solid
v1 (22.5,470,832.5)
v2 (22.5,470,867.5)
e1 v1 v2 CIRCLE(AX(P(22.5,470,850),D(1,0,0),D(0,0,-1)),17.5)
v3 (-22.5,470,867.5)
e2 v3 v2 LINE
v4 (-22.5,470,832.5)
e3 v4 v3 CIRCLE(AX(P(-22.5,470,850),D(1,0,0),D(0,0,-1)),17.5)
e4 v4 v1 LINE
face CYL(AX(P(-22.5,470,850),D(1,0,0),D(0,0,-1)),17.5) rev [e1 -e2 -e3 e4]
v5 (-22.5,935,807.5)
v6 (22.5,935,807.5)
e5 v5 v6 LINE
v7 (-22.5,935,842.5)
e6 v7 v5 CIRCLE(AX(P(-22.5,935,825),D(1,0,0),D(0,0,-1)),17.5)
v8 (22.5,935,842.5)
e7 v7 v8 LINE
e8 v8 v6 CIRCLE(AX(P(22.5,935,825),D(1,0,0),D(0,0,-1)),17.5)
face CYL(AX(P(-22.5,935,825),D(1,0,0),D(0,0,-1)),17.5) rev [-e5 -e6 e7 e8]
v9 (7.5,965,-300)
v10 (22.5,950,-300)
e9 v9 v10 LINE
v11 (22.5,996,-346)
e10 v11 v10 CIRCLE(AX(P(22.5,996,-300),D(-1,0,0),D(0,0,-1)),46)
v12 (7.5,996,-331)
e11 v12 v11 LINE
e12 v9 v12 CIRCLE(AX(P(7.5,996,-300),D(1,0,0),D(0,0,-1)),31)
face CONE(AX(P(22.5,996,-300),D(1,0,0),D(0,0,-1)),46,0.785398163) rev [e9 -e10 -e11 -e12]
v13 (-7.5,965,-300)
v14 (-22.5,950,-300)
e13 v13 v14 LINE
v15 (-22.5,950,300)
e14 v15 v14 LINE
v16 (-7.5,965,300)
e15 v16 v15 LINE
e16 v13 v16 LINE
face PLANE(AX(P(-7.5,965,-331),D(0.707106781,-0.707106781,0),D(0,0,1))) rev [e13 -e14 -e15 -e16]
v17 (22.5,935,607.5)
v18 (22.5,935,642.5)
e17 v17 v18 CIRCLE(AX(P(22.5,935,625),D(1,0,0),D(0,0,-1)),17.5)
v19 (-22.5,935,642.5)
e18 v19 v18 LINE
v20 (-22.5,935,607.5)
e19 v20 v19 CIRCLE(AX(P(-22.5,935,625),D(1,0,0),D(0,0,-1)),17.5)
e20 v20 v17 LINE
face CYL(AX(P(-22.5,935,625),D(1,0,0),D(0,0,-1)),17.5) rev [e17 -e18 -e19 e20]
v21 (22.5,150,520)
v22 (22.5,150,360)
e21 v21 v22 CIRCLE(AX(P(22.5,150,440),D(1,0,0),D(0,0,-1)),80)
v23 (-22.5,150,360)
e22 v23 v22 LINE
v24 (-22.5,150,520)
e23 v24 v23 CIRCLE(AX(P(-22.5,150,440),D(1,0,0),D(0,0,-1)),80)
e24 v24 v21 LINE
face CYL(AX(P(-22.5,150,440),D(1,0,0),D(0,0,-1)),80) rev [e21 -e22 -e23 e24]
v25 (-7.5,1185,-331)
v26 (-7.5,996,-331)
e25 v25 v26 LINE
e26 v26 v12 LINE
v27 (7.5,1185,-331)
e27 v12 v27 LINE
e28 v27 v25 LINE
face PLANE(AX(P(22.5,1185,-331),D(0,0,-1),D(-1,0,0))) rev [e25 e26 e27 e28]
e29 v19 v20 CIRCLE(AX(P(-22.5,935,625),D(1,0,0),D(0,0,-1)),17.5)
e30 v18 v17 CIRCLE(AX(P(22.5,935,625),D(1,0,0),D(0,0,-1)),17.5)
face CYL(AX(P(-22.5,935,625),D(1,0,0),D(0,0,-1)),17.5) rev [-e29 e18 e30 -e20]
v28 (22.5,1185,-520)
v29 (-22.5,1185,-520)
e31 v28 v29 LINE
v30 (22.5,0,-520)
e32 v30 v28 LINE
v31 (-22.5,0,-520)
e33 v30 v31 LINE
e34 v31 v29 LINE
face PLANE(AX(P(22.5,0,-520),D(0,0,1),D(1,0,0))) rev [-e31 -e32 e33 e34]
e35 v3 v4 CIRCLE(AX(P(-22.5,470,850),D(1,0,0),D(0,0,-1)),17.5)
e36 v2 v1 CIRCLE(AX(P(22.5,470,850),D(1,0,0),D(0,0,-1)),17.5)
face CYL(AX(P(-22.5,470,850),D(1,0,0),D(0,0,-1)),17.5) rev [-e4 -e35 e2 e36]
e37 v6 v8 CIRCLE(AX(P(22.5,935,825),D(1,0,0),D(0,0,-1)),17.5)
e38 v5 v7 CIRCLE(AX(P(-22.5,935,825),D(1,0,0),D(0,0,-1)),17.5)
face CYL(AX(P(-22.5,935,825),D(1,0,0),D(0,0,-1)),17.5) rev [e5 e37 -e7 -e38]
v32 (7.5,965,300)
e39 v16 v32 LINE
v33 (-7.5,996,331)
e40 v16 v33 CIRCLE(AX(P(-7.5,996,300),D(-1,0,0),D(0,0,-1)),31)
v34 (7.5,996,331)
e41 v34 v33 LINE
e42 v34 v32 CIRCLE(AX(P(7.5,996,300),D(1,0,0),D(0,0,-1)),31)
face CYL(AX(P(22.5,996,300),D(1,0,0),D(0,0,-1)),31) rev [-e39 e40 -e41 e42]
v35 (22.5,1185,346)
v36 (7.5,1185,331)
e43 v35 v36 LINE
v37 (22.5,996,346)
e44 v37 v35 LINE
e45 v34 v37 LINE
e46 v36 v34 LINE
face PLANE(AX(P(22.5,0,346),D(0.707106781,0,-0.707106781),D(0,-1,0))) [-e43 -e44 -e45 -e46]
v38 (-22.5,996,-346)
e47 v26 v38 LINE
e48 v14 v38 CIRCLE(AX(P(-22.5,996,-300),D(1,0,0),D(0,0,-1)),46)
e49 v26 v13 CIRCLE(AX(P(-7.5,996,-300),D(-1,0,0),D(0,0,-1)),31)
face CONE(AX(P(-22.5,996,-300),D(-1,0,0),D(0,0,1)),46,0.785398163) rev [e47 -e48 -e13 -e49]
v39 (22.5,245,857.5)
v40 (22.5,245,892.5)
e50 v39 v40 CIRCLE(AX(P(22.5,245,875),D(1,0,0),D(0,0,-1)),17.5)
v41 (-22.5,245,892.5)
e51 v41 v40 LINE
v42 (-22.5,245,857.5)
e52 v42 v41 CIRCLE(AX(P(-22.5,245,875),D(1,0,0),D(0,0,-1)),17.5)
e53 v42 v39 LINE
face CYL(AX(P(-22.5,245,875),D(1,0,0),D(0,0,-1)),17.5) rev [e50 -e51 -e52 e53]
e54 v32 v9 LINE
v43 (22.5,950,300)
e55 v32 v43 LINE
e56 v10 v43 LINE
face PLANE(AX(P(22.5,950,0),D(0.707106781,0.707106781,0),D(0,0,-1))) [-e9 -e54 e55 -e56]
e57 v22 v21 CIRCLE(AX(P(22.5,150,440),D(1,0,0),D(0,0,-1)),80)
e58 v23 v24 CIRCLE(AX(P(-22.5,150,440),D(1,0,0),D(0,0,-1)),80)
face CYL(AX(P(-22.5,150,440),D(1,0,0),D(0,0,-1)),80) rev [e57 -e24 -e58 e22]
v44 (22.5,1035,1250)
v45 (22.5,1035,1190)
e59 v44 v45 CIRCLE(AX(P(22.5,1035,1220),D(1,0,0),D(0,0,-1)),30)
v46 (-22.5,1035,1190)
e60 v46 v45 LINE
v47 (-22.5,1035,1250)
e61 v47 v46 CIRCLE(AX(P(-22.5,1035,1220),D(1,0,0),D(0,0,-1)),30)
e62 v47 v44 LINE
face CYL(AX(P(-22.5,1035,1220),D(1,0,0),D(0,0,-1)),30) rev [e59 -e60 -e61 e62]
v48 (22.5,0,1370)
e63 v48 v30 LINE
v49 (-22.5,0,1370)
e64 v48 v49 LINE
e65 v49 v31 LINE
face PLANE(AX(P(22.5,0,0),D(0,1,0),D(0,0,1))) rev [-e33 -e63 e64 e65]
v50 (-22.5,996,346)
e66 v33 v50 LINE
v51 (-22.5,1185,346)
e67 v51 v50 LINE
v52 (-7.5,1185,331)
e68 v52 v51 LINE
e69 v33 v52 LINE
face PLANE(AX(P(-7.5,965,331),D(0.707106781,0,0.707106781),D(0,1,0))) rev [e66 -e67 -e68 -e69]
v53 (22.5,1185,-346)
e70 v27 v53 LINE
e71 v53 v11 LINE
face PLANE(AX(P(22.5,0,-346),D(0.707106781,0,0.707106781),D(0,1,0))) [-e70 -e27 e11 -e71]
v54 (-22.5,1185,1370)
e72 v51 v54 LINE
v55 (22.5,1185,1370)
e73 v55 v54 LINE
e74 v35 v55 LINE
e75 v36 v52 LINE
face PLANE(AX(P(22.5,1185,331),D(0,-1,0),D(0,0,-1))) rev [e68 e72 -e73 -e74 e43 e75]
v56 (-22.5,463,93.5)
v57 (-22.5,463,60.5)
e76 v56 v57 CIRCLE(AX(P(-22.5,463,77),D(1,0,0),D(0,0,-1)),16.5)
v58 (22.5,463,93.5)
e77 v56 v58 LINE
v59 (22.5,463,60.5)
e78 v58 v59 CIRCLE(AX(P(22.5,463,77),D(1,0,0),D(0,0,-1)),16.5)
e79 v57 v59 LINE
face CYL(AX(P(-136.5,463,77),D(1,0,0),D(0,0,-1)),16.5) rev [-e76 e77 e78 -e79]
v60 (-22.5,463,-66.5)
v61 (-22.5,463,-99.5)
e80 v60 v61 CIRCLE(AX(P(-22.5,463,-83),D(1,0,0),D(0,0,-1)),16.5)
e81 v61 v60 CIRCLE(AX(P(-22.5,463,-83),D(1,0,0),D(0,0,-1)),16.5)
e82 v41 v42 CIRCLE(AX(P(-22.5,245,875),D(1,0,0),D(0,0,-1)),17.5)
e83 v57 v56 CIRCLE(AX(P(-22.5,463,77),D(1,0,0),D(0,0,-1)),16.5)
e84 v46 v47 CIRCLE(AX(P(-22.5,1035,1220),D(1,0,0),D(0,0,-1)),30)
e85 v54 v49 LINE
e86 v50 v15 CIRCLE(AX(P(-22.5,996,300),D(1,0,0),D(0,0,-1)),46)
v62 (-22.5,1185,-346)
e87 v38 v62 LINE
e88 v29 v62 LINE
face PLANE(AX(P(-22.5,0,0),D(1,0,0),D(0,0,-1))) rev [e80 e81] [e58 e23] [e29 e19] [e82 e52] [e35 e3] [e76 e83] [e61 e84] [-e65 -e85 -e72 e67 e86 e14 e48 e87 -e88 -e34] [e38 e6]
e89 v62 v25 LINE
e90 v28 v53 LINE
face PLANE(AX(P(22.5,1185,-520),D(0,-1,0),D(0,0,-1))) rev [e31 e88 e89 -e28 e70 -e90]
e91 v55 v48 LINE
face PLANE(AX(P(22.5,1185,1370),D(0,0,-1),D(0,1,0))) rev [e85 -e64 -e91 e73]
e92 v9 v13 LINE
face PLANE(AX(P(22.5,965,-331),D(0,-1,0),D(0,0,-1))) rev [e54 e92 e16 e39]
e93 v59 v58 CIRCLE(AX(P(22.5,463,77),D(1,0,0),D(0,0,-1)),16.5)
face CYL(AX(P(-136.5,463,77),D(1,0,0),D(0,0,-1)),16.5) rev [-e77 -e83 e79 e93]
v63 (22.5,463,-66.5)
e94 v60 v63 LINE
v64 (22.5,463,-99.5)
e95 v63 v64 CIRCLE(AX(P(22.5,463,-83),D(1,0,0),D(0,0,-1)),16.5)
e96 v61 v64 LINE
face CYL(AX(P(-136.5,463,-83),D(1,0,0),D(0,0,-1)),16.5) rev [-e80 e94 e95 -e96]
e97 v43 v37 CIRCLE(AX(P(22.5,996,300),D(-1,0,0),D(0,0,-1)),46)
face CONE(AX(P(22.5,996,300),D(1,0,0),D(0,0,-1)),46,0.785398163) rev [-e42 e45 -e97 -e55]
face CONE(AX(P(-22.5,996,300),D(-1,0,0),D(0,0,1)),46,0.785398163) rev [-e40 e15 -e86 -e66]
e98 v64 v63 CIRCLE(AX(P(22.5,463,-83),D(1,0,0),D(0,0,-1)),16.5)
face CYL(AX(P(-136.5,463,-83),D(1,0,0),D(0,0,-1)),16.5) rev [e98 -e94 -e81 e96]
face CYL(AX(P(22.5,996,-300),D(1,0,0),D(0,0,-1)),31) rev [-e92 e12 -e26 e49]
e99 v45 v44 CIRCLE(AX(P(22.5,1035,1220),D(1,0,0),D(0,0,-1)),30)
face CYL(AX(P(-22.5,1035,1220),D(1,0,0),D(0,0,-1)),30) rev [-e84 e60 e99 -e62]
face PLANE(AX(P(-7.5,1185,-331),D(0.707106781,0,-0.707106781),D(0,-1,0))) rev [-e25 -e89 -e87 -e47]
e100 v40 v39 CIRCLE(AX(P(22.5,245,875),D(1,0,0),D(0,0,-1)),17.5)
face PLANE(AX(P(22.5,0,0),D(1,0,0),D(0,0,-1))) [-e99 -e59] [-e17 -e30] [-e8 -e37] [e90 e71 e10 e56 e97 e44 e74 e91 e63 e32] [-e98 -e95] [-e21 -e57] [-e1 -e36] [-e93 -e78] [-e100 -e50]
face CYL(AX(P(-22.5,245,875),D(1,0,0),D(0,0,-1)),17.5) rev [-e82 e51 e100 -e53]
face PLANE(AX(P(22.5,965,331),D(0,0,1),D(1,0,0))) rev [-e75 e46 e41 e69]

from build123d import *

# Parameters (mm, degrees)
BOSS_EXTRUDE1_DEPTH = 22.5
SKETCH2_R           = 30
SKETCH2_R_2         = 17.5
SKETCH2_R_3         = 80
CUT_EXTRUDE1_DEPTH  = 1812.9464672
FILLET1_R           = 31
CHAMFER1_SIZE       = 15
SKETCH3_R           = 16.5
CUT_EXTRUDE2_DEPTH  = 159


with BuildPart() as part:
    # Sketch1 → Boss-Extrude1 (new, symmetric)
    with BuildSketch(Plane(origin=(0, 0, 0), x_dir=(0, 0, -1), z_dir=(1, 0, 0))):
        Polygon((0, 0), (520, 0), (520, 1185), (331, 1185), (331, 965), (-331, 965), (-331, 1185), (-1370, 1185), (-1370, 0), align=None)
    extrude(amount=BOSS_EXTRUDE1_DEPTH, both=True)

    # Sketch2 → Cut-Extrude1 (cut, through all)
    with BuildSketch(Plane(origin=(22.5, 0, 0), x_dir=(0, 0, -1), z_dir=(1, 0, 0))):
        with Locations((-1220, 1035)):
            Circle(SKETCH2_R)
        with Locations((-825, 935)):
            Circle(SKETCH2_R_2)
        with Locations((-625, 935)):
            Circle(SKETCH2_R_2)
        with Locations((-850, 470)):
            Circle(SKETCH2_R_2)
        with Locations((-875, 245)):
            Circle(SKETCH2_R_2)
        with Locations((-440, 150)):
            Circle(SKETCH2_R_3)
    extrude(amount=-CUT_EXTRUDE1_DEPTH, mode=Mode.SUBTRACT)

    # Fillet1
    fillet1_edges = [part.edges().sort_by_distance(p)[0] for p in [
        (0, 965, 331),
        (0, 965, -331),
    ]]
    fillet(fillet1_edges, radius=FILLET1_R)

    # Chamfer1
    chamfer1_edges = [part.edges().sort_by_distance(p)[0] for p in [
        (-22.5, 1090.5, -331),
        (22.5, 1090.5, -331),
        (-22.5, 965, 0),
        (22.5, 965, 0),
        (-22.5, 1090.5, 331),
        (22.5, 1090.5, 331),
        (-22.5, 974.079689783, -321.920310217),
        (22.5, 974.079689783, -321.920310217),
        (-22.5, 974.079689783, 321.920310217),
        (22.5, 974.079689783, 321.920310217),
    ]]
    chamfer(chamfer1_edges, length=CHAMFER1_SIZE)

    # Sketch3 → Cut-Extrude2 (cut)
    with BuildSketch(Plane(origin=(22.5, 0, 0), x_dir=(0, 0, -1), z_dir=(1, 0, 0))):
        with Locations((-77, 463)):
            Circle(SKETCH3_R)
        with Locations((83, 463)):
            Circle(SKETCH3_R)
    extrude(amount=-CUT_EXTRUDE2_DEPTH, mode=Mode.SUBTRACT)


solid = part.part
